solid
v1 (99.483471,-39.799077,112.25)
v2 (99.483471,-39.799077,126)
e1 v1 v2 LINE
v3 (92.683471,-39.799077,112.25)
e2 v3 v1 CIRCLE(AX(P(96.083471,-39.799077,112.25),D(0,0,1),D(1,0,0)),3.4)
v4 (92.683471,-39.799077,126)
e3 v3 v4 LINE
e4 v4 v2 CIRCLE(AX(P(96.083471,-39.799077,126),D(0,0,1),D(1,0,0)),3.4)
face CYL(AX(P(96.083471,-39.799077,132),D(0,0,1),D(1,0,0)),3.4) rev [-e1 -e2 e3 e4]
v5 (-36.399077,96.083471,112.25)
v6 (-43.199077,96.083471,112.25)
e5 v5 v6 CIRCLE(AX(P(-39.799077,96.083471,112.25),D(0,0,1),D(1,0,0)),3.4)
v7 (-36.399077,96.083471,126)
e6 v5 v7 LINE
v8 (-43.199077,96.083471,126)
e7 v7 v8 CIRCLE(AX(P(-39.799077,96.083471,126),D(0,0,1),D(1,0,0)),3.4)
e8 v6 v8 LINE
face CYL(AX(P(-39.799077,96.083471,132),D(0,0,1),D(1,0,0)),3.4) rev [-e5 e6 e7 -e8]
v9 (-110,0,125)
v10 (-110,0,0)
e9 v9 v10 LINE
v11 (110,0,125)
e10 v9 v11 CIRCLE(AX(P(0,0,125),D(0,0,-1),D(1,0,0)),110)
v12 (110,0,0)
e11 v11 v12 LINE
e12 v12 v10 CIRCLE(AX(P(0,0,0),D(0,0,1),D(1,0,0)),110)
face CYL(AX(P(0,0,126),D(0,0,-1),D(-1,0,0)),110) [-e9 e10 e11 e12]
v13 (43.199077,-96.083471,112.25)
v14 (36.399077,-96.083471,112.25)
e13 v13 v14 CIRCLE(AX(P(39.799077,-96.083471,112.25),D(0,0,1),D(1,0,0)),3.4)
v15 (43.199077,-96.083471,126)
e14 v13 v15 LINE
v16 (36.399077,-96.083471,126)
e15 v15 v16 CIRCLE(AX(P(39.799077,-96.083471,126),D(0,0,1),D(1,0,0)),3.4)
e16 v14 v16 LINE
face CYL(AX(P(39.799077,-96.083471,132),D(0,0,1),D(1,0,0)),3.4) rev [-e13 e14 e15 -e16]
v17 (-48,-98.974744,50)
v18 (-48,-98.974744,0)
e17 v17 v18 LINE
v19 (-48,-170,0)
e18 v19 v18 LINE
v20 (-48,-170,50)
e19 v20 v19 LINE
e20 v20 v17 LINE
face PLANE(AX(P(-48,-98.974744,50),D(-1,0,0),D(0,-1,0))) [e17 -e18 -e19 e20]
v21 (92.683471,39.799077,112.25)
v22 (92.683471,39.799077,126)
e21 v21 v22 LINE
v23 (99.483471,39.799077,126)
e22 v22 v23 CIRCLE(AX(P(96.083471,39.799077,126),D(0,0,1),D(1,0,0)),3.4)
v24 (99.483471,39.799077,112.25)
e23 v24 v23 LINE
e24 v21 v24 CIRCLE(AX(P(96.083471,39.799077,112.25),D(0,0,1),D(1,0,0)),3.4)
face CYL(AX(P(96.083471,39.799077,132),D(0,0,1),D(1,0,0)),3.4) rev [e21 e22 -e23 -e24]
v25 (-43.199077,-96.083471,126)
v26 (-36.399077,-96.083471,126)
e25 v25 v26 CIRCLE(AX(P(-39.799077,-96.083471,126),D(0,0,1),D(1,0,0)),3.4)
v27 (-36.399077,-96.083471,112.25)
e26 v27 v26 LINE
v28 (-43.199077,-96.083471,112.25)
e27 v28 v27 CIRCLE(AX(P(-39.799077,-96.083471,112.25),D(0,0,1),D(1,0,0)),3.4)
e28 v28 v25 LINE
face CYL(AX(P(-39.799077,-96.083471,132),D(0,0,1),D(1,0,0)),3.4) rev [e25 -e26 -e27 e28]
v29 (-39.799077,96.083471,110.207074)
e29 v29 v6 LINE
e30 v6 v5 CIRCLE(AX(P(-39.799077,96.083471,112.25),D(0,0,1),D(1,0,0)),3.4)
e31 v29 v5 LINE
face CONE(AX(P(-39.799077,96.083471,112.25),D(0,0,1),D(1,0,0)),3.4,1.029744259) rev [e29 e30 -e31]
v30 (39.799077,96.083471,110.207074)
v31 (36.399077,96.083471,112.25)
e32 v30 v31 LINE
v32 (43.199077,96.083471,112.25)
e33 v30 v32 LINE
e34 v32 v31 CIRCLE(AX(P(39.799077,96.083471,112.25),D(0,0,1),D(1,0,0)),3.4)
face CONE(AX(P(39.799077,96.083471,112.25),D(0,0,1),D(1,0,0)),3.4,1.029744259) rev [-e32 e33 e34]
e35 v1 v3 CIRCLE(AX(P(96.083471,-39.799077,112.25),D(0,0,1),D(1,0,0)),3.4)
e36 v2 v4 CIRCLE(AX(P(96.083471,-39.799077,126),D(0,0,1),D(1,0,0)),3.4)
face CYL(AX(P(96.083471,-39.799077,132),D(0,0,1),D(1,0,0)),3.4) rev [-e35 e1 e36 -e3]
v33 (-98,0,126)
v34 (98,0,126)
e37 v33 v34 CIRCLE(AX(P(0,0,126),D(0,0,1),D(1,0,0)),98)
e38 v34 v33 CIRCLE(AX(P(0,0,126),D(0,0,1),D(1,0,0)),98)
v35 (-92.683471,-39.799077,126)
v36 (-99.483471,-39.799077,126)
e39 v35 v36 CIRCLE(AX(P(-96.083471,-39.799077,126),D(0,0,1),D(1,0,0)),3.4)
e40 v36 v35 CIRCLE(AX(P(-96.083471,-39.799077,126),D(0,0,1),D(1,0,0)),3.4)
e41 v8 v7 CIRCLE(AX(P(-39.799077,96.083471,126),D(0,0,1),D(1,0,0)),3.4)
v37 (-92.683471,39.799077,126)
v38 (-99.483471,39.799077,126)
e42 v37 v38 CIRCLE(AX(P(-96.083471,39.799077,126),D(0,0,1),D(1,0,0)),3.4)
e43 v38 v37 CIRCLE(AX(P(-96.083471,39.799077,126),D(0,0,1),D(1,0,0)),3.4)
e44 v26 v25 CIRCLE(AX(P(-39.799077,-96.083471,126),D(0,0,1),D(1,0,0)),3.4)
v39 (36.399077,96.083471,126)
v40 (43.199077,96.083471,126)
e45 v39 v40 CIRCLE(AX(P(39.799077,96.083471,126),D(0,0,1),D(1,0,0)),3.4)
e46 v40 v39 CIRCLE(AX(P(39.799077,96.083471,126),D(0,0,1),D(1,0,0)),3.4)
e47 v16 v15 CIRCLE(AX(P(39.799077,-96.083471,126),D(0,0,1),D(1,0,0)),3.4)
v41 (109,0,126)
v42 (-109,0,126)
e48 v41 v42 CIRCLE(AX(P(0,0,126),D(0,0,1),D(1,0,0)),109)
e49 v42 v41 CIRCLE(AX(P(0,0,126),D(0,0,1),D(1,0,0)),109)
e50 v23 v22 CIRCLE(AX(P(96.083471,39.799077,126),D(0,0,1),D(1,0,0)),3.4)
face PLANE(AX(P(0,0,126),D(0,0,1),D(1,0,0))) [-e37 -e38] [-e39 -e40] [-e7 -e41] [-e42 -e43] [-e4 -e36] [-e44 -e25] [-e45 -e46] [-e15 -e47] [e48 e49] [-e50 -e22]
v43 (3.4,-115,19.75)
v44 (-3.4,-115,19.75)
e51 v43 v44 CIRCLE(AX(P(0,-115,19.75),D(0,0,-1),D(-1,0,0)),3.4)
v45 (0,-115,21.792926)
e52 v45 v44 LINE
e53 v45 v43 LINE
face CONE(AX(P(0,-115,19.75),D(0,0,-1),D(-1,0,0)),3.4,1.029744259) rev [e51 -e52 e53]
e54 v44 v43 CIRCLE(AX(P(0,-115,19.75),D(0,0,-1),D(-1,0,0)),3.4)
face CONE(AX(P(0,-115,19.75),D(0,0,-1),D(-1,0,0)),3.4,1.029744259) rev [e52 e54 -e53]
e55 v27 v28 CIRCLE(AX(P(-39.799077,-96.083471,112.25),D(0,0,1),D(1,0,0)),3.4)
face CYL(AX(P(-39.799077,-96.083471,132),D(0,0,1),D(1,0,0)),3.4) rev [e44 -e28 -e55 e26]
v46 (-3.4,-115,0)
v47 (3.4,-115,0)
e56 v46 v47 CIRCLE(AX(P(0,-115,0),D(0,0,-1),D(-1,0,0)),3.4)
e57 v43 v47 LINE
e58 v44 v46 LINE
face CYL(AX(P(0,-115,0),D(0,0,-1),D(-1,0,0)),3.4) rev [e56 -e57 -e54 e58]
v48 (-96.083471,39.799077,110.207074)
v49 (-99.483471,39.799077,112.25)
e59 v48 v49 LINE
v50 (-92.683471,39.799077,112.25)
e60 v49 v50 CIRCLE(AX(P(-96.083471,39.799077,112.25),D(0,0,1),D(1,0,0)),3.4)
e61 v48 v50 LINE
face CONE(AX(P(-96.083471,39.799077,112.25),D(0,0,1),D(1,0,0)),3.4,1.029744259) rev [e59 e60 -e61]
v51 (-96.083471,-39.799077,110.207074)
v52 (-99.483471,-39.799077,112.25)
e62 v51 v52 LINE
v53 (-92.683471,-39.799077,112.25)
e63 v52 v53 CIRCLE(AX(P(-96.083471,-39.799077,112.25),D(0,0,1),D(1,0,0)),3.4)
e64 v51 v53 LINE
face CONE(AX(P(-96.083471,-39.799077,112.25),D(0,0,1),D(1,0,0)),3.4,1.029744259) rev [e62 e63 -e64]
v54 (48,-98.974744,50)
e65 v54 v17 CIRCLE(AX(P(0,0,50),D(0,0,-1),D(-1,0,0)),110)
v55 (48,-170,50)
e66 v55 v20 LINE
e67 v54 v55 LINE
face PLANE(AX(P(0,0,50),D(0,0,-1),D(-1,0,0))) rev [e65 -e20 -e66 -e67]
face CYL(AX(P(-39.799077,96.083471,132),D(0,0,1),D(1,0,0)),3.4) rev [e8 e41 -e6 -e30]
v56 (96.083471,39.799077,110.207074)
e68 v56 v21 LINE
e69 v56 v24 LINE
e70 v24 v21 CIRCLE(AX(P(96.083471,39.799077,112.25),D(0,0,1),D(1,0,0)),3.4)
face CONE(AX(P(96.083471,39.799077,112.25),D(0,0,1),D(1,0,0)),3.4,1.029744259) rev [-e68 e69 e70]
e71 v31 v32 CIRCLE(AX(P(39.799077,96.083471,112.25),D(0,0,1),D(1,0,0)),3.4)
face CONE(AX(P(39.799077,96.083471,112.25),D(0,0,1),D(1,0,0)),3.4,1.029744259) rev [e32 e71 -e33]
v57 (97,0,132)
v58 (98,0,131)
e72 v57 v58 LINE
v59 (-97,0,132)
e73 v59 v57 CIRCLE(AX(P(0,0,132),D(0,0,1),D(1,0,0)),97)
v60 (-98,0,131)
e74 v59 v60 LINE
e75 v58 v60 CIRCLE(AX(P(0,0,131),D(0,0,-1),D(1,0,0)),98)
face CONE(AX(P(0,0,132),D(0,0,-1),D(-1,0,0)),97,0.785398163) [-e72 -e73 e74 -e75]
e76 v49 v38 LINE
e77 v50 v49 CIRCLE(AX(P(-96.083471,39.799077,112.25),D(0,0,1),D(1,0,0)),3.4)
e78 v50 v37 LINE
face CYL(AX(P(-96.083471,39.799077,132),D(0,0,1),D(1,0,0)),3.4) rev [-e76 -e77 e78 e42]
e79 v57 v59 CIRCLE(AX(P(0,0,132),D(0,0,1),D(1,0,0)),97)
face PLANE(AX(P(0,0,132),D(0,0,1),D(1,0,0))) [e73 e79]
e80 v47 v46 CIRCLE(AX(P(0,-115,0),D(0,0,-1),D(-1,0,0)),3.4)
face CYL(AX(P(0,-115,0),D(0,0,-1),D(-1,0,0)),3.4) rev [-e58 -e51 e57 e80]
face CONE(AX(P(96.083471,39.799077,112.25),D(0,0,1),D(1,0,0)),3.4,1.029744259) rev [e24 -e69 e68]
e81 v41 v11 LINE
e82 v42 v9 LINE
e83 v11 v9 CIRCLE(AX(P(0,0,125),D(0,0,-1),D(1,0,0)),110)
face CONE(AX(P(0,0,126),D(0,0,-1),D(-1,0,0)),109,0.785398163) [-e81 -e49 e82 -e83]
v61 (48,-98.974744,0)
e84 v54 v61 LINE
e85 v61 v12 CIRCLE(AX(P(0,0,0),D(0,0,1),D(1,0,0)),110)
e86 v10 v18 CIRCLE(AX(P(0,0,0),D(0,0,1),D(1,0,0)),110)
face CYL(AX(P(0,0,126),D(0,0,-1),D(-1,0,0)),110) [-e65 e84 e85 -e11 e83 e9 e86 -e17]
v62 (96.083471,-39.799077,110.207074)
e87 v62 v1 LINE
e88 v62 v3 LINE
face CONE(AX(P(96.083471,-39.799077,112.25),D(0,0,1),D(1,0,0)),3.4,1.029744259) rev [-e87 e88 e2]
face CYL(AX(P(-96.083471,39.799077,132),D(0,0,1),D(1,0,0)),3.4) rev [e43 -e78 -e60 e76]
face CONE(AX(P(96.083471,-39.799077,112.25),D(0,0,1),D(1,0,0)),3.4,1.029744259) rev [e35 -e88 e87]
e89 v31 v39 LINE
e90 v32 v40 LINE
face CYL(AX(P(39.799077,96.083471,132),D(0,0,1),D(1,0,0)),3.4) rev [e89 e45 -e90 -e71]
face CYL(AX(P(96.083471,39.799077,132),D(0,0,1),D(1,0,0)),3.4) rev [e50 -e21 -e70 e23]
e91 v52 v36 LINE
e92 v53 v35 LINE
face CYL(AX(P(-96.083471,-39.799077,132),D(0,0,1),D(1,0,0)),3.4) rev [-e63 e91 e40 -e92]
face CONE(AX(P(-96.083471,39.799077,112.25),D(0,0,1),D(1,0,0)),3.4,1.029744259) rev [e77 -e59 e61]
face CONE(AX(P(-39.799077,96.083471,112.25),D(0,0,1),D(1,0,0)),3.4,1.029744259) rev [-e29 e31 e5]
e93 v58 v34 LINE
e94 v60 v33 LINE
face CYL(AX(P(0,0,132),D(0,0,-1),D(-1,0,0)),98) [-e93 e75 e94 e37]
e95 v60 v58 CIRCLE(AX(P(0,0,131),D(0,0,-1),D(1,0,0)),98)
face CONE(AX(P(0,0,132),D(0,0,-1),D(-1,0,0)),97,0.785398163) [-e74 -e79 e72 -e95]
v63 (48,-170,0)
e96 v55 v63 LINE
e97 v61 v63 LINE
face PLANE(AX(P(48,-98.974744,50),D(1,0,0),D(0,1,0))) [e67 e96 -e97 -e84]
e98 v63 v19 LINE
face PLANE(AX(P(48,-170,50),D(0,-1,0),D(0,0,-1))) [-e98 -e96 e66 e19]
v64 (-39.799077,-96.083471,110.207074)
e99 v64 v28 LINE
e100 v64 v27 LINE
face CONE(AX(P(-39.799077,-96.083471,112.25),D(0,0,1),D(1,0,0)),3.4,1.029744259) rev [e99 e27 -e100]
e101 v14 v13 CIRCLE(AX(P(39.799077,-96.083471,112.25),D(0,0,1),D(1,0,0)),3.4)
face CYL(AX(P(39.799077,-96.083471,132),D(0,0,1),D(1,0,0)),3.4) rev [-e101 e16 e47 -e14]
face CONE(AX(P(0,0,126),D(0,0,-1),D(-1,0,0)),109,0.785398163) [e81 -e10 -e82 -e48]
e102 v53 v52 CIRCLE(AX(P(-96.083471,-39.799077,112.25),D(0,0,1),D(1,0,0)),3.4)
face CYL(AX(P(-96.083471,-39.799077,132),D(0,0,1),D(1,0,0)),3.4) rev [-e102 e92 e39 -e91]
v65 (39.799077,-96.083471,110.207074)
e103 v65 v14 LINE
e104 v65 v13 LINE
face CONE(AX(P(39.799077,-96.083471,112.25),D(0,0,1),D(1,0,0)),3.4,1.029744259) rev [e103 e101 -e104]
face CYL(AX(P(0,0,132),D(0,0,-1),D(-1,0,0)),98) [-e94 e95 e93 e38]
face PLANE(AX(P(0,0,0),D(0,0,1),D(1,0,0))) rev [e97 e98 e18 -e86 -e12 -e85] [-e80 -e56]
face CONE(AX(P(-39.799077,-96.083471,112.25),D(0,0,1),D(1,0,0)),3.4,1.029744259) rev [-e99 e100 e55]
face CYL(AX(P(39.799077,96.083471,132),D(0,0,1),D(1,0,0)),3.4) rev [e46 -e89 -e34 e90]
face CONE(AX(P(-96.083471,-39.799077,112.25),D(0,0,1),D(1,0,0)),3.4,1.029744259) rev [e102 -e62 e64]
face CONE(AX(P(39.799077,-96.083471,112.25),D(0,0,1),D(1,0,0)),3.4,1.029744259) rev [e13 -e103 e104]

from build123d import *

# Parameters (mm, degrees)
SKETCH_1_R             = 110
EXTRUDE_1_DEPTH        = 126
SKETCH_2_R             = 98
EXTRUDE_2_DEPTH        = 6
SKETCH_3_W             = 96
SKETCH_3_H             = 71.025255747
EXTRUDE_3_DEPTH        = 50
CHAMFER_1_SIZE         = 1
HOLE_WIZARD_M8_1_D     = 6.8
HOLE_WIZARD_M8_1_DEPTH = 19.75
HOLE_WIZARD_M8_1_TIP   = 2.042926105
HOLE_WIZARD_M8_2_D     = 6.8
HOLE_WIZARD_M8_2_DEPTH = 19.75
HOLE_WIZARD_M8_2_TIP   = 2.042926105


with BuildPart() as part:
    # 草图1 → 凸台-拉伸1 (new body)
    with BuildSketch(Plane.XY):
        Circle(SKETCH_1_R)
    extrude(amount=EXTRUDE_1_DEPTH)

    # 草图2 → 凸台-拉伸2 (add)
    with BuildSketch(Plane.XY.offset(126)):
        Circle(SKETCH_2_R)
    extrude(amount=EXTRUDE_2_DEPTH)

    # 草图3 → 凸台-拉伸3 (add)
    with BuildSketch(Plane(origin=(0, 0, 0), x_dir=(-1, 0, 0), z_dir=(0, 0, -1))):
        with Locations((0, -134.487372127)):
            Rectangle(SKETCH_3_W, SKETCH_3_H)
    extrude(amount=-EXTRUDE_3_DEPTH)

    # 倒角1
    chamfer_1_edges = [part.edges().sort_by_distance(p)[0] for p in [
        (-110, 0, 126),
        (-98, 0, 132),
    ]]
    chamfer(chamfer_1_edges, length=CHAMFER_1_SIZE)

    # M8 螺纹孔1
    with Locations(Plane(origin=(0, 0, 0), x_dir=(-1, 0, 0), z_dir=(0, 0, -1))):
        with Locations((0, 115), (81.317279836, 81.317279836), (115, 0), (81.317279836, -81.317279836), (0, -115), (-81.317279836, -81.317279836), (-115, 0), (-81.317279836, 81.317279836)):
            Hole(HOLE_WIZARD_M8_1_D / 2, depth=HOLE_WIZARD_M8_1_DEPTH)
            with Locations((0, 0, -(HOLE_WIZARD_M8_1_DEPTH + HOLE_WIZARD_M8_1_TIP / 2))):  # 118° drill point
                Cone(0, HOLE_WIZARD_M8_1_D / 2, HOLE_WIZARD_M8_1_TIP, mode=Mode.SUBTRACT)

    # M8 螺纹孔2
    with Locations(Plane.XY.offset(132)):
        with Locations((39.799076966, 96.083471381), (96.083471381, 39.799076966), (96.083471381, -39.799076966), (39.799076966, -96.083471381), (-39.799076966, -96.083471381), (-96.083471381, -39.799076966), (-96.083471381, 39.799076966), (-39.799076966, 96.083471381)):
            Hole(HOLE_WIZARD_M8_2_D / 2, depth=HOLE_WIZARD_M8_2_DEPTH)
            with Locations((0, 0, -(HOLE_WIZARD_M8_2_DEPTH + HOLE_WIZARD_M8_2_TIP / 2))):  # 118° drill point
                Cone(0, HOLE_WIZARD_M8_2_D / 2, HOLE_WIZARD_M8_2_TIP, mode=Mode.SUBTRACT)


solid = part.part
